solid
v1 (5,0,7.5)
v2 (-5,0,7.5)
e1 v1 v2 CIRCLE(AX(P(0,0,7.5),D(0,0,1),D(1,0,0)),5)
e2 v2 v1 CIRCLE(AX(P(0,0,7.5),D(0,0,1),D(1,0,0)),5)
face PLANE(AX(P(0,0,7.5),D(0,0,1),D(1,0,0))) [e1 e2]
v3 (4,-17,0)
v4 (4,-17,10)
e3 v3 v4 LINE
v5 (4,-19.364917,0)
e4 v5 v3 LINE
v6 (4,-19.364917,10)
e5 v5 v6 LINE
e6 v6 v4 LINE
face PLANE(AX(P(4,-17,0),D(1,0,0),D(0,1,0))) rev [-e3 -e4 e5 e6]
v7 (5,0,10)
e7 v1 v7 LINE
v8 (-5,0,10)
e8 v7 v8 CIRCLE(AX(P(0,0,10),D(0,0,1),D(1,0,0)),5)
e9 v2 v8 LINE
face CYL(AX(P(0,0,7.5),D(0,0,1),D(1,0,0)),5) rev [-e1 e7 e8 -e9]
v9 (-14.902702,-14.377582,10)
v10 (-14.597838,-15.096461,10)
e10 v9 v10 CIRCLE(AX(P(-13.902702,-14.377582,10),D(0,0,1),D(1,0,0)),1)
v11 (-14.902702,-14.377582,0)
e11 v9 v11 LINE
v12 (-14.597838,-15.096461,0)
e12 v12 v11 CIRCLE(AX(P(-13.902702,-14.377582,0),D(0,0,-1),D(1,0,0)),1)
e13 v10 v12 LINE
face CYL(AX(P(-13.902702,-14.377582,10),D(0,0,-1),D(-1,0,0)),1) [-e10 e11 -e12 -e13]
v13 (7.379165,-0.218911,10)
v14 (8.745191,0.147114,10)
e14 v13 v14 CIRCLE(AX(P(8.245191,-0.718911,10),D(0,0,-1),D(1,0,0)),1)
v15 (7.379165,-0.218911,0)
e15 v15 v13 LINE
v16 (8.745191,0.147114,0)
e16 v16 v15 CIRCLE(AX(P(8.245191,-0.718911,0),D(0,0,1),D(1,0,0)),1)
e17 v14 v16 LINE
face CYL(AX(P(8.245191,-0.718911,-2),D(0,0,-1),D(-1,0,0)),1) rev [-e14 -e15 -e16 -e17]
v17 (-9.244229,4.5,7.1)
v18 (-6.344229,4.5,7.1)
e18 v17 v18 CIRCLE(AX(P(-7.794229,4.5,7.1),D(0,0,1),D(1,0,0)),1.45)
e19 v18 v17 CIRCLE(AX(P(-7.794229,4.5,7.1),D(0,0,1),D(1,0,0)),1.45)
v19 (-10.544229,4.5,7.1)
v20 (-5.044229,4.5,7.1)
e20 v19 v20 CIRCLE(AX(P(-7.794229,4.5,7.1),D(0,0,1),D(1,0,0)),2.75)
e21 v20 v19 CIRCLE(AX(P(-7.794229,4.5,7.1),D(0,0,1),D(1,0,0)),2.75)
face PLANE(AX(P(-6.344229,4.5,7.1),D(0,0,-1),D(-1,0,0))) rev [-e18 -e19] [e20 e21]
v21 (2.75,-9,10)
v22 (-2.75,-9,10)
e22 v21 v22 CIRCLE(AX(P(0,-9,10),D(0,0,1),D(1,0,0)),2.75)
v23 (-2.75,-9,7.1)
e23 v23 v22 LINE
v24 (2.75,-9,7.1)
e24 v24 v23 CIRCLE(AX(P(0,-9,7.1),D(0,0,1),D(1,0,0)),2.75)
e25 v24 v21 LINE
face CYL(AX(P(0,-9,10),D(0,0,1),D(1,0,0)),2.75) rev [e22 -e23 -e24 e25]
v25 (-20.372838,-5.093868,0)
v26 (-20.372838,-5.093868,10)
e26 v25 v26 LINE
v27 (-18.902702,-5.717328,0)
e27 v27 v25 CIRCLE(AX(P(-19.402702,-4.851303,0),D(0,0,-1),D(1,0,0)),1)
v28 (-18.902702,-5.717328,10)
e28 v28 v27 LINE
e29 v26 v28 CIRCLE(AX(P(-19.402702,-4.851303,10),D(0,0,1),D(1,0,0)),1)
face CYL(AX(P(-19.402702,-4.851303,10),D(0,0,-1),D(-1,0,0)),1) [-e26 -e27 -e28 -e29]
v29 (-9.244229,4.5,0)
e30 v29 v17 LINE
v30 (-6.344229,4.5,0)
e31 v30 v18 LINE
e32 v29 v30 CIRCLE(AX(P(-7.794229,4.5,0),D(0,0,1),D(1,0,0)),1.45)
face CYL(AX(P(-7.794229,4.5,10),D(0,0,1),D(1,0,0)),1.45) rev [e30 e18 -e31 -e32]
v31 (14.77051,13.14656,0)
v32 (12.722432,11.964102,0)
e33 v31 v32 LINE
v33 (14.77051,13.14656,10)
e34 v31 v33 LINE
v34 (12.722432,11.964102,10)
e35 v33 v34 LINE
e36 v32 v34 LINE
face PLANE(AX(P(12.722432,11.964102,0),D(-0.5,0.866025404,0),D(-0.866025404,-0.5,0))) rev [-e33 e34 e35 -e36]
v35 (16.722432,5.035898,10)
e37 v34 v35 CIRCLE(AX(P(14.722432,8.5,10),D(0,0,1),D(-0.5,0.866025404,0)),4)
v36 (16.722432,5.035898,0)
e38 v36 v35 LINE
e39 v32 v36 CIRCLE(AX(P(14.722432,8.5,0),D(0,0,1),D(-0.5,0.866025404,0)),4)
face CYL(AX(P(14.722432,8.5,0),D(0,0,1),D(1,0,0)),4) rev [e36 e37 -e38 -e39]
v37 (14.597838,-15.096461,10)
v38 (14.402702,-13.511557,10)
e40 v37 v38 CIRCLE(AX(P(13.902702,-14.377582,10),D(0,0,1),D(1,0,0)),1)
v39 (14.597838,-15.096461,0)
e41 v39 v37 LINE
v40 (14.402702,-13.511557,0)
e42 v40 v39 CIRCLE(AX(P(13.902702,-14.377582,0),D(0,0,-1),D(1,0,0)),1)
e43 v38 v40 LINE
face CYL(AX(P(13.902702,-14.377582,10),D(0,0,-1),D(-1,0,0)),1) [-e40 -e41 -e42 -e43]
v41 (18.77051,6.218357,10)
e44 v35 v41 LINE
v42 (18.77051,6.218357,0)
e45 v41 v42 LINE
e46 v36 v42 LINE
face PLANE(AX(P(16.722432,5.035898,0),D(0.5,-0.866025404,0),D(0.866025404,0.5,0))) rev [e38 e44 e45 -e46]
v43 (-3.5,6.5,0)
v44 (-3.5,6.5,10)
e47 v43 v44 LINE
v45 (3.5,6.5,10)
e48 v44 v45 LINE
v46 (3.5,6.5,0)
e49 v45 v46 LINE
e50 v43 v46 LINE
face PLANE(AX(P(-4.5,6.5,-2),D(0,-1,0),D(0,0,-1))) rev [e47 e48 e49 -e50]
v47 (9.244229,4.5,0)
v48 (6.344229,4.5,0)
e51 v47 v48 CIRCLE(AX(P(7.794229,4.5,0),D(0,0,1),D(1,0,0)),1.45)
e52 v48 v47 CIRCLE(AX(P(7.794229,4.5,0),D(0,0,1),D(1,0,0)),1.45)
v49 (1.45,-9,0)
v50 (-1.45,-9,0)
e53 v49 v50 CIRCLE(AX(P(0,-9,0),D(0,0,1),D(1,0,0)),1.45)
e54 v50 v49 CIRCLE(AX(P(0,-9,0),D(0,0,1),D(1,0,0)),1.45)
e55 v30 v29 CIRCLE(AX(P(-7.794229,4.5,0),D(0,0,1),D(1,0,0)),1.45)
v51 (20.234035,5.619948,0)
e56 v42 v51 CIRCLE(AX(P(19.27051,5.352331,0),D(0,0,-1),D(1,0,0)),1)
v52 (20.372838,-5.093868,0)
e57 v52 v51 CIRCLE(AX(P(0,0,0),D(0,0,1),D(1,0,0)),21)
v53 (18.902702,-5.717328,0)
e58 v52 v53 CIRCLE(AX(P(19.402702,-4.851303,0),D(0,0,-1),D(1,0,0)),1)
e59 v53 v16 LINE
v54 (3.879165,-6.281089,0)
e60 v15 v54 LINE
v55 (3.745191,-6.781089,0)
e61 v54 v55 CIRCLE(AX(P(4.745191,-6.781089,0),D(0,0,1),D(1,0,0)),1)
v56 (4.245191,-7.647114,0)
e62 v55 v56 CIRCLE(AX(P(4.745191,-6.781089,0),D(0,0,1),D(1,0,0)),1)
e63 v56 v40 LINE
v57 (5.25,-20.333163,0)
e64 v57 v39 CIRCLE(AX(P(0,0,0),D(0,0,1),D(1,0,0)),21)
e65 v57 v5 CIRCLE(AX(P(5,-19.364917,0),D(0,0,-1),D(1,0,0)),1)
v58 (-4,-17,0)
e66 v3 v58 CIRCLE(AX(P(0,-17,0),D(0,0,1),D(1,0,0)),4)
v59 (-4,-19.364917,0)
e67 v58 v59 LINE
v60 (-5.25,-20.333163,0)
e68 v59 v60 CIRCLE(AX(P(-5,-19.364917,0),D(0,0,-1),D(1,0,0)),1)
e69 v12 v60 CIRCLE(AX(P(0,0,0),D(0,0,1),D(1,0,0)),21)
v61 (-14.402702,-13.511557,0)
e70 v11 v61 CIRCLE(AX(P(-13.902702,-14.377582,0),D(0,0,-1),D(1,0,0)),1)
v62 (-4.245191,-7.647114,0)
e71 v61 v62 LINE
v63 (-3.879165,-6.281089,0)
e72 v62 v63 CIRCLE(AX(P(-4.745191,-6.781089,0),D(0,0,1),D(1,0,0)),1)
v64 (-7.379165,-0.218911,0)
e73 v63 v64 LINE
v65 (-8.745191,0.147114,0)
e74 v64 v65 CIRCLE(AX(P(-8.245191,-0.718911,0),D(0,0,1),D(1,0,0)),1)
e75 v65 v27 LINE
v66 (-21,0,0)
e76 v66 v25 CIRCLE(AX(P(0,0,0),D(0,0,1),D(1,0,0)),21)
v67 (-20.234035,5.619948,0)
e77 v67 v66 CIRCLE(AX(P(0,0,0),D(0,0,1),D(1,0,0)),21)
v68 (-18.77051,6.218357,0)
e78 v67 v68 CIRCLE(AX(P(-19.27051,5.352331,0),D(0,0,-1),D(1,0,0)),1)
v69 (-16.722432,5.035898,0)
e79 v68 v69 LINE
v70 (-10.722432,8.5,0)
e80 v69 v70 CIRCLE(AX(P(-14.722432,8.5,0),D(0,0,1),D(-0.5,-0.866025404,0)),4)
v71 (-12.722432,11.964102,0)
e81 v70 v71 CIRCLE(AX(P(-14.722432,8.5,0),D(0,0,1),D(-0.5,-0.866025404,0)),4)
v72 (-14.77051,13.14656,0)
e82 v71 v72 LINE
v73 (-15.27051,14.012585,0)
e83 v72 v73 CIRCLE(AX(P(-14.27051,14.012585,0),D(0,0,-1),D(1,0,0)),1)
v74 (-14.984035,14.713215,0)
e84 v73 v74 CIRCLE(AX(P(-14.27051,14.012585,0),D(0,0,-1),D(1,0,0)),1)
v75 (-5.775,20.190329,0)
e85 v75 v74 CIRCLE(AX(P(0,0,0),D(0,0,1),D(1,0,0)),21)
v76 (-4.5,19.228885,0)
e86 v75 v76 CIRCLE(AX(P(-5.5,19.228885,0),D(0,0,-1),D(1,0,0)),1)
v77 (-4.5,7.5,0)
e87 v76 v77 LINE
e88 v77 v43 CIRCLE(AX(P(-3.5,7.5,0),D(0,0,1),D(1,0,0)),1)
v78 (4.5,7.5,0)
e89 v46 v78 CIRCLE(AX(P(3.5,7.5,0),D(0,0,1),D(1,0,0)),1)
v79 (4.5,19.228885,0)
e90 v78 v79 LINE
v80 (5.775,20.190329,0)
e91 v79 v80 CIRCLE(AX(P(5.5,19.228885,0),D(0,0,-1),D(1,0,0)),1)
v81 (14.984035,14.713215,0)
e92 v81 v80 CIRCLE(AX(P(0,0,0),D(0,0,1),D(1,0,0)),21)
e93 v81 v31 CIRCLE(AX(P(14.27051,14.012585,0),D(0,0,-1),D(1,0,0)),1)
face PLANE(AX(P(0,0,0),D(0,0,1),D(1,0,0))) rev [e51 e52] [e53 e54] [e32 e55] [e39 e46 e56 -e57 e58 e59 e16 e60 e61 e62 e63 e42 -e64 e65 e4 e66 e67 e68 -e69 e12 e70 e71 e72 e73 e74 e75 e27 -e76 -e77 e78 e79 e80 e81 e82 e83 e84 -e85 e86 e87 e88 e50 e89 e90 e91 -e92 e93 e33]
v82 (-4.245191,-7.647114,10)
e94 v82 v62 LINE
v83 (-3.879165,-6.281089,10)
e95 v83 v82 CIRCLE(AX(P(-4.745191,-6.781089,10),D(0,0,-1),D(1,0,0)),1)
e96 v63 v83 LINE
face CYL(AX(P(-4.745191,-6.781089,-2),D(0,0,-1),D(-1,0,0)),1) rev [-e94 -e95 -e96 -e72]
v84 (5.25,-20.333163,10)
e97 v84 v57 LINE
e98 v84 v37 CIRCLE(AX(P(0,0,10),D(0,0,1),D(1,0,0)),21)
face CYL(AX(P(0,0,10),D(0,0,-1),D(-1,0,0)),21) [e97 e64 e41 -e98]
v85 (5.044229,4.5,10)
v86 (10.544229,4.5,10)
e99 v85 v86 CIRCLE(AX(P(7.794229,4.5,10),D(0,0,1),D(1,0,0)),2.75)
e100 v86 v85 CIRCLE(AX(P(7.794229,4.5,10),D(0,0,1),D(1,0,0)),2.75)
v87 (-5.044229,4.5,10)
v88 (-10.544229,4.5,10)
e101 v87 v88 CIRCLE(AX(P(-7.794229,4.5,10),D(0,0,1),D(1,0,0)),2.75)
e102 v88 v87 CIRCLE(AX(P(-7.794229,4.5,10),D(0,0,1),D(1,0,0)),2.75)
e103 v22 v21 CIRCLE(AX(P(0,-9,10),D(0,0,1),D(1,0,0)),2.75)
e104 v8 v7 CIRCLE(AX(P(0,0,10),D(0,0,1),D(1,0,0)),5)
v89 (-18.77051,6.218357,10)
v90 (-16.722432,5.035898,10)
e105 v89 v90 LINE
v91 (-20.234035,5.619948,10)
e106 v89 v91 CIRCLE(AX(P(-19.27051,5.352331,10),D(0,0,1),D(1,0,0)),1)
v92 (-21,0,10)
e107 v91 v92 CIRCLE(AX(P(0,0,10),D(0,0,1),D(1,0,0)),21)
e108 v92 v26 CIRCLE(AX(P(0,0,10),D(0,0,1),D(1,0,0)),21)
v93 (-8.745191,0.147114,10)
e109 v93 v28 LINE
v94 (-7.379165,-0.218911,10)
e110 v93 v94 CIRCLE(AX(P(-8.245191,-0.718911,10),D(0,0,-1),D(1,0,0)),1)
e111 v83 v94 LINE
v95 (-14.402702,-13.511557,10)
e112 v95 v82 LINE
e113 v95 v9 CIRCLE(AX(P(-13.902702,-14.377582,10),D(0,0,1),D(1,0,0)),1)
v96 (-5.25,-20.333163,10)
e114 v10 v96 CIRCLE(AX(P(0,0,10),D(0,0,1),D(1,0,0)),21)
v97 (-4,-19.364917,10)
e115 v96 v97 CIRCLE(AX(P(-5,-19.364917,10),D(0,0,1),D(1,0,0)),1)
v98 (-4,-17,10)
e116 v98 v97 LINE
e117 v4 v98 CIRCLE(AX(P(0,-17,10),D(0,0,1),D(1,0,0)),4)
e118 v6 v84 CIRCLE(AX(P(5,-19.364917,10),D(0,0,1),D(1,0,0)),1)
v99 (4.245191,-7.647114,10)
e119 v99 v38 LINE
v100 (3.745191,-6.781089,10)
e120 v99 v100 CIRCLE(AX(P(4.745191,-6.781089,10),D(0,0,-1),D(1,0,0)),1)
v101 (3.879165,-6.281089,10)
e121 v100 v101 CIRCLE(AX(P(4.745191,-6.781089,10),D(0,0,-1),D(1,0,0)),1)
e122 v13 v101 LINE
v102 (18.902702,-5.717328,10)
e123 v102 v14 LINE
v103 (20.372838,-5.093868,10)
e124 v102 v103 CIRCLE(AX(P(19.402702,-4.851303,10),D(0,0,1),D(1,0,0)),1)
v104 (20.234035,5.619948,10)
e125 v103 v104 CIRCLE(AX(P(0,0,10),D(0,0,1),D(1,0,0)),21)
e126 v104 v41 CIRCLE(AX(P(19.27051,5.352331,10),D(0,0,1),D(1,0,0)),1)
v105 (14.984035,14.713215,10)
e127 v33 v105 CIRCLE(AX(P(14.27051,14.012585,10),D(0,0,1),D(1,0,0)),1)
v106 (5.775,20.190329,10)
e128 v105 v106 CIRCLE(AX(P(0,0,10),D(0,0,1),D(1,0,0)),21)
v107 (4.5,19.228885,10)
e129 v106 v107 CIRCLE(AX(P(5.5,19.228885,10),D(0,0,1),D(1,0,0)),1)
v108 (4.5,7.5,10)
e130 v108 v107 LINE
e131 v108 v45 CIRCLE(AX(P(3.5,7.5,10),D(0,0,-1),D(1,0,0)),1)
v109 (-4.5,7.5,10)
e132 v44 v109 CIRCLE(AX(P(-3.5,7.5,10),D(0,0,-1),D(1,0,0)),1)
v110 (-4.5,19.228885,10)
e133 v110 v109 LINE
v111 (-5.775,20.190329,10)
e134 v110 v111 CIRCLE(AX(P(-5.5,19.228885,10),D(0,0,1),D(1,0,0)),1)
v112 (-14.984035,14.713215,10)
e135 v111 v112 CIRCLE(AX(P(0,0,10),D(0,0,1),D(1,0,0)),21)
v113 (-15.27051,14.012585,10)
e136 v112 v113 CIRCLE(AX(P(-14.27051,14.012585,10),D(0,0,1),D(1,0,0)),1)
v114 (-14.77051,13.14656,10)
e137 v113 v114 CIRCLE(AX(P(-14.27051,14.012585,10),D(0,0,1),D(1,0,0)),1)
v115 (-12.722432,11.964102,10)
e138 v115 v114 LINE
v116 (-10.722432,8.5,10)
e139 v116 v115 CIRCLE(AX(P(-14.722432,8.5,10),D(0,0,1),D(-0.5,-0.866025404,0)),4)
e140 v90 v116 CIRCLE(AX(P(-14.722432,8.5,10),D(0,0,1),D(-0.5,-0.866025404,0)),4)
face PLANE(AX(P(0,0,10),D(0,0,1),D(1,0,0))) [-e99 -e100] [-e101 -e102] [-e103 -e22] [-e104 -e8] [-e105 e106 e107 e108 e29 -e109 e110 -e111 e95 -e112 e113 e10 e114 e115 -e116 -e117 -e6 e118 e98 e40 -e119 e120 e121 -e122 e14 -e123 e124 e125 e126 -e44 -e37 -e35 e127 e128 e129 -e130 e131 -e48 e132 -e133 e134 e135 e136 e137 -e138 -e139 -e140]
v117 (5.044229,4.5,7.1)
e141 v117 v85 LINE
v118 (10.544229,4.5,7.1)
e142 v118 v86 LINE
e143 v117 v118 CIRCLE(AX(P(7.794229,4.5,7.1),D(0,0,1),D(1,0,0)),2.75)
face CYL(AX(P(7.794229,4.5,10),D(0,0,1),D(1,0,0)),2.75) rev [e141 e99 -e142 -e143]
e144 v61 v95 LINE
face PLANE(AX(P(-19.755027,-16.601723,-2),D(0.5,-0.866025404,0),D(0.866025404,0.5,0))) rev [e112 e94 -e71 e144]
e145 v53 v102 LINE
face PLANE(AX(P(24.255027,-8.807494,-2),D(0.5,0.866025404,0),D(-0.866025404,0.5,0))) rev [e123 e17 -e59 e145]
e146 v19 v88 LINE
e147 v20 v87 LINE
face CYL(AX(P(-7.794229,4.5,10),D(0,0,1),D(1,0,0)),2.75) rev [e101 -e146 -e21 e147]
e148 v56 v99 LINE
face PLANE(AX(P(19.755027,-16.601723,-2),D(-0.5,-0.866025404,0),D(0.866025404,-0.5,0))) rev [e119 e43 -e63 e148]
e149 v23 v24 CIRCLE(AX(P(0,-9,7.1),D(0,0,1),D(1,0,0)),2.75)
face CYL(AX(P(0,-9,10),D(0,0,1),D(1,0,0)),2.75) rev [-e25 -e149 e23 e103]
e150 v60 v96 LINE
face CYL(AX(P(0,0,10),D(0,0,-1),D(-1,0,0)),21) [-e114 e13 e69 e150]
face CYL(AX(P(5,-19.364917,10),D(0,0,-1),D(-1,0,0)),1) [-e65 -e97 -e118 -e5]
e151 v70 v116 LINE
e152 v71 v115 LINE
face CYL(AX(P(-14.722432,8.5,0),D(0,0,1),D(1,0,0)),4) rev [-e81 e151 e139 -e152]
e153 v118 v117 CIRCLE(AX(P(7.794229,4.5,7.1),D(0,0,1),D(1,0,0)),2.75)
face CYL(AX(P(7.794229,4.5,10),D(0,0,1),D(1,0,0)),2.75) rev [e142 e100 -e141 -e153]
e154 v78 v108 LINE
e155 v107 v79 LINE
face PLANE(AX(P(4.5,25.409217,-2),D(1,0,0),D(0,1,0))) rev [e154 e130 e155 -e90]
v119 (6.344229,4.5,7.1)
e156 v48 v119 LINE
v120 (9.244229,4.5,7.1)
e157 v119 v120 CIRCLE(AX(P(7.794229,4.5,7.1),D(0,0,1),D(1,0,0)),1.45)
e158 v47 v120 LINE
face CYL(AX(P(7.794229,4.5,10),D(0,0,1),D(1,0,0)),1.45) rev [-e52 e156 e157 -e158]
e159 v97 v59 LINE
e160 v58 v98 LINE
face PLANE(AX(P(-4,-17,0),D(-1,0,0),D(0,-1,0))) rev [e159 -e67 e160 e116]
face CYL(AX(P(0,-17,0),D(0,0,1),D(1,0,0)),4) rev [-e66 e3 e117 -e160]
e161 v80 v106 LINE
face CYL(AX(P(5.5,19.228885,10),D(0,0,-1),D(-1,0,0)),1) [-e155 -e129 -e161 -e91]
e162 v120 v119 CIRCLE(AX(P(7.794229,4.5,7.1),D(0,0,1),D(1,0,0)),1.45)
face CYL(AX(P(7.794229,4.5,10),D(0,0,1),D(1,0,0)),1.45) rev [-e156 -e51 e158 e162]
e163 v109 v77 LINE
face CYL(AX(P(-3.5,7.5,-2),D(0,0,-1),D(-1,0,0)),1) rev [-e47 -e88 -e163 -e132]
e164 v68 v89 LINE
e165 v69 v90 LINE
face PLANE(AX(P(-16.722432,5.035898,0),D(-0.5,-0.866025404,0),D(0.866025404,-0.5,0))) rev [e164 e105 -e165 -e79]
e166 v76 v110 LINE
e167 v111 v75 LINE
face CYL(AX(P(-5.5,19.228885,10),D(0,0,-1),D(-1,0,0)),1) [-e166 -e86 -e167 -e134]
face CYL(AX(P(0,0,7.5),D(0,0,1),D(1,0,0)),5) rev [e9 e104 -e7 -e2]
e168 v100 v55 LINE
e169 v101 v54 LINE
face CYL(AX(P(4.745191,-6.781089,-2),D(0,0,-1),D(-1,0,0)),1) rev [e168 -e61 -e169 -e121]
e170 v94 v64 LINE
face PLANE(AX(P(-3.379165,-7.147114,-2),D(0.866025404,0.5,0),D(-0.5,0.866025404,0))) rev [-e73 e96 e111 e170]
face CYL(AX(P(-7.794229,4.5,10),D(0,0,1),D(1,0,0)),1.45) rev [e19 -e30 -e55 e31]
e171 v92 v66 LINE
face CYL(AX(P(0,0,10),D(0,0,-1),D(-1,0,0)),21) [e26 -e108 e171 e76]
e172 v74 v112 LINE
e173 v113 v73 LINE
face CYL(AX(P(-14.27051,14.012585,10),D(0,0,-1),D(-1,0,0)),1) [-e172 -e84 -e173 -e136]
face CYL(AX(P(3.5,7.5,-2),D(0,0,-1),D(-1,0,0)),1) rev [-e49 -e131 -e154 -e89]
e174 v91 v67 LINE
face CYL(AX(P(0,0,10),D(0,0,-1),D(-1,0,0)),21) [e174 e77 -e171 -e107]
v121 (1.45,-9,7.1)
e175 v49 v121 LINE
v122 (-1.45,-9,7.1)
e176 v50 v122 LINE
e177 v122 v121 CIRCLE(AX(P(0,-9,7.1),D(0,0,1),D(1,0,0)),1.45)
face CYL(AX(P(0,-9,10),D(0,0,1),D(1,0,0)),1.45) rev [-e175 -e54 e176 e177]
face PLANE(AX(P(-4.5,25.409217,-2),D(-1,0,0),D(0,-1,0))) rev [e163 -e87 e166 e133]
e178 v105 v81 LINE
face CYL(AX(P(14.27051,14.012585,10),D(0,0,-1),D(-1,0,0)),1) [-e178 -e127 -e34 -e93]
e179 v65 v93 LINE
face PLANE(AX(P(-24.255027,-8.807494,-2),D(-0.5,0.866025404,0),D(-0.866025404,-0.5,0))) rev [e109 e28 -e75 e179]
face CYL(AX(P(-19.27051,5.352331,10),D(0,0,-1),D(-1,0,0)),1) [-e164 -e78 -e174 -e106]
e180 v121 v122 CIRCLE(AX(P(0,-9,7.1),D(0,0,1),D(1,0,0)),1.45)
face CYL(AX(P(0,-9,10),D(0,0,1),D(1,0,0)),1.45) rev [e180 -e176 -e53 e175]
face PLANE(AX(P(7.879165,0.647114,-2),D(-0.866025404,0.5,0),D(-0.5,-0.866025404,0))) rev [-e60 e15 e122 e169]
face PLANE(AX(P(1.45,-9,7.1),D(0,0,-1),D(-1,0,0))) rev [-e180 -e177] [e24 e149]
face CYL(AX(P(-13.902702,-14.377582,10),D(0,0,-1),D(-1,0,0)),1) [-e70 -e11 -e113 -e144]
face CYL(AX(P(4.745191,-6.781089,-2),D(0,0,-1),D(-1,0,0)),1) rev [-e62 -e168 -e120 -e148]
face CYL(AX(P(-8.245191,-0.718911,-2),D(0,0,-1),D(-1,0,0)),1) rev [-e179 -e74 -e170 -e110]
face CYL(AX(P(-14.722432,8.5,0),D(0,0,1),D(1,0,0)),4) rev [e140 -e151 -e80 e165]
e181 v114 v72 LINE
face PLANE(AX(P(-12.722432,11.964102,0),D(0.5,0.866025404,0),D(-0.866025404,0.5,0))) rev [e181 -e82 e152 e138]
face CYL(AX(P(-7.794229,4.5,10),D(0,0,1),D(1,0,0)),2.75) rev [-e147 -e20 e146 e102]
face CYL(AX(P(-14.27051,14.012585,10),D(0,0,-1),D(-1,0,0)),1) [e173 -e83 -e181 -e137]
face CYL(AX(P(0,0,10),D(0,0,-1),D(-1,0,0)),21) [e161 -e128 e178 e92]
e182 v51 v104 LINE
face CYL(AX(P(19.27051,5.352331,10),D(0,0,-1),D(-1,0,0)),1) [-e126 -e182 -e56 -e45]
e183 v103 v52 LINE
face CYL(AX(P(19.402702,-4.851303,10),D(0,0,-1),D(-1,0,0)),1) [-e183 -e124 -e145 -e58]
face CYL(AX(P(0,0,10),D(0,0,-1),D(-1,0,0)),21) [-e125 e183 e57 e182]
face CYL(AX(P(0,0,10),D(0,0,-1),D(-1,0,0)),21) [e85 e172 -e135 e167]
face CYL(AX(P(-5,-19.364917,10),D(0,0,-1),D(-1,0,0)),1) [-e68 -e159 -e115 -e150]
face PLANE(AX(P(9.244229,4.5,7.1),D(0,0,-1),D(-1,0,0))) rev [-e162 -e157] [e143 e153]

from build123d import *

# Parameters (mm, degrees)
SKETCH1_R                                            = 21
BOSS_EXTRUDE1_DEPTH                                  = 10
SKETCH2_W                                            = 9
SKETCH2_H                                            = 18.909216571
CUT_EXTRUDE1_DEPTH                                   = 12
FILLET1_R                                            = 1
CIRPATTERN1_COUNT                                    = 3
FILLET1_OF_CIRPATTERN1_R                             = 1
CBORE_FOR_M2_5_HEX_SOCKET_HEAD_CAP_SCREW_D           = 2.9
CBORE_FOR_M2_5_HEX_SOCKET_HEAD_CAP_SCREW_CBORE_D     = 5.5
CBORE_FOR_M2_5_HEX_SOCKET_HEAD_CAP_SCREW_CBORE_DEPTH = 2.9
CIRPATTERN2_COUNT                                    = 3
CUT_EXTRUDE2_DEPTH                                   = 32.336879232
FILLET2_R                                            = 1
CIRPATTERN3_COUNT                                    = 3
FILLET2_OF_CIRPATTERN3_R                             = 1
SKETCH7_R                                            = 5
CUT_EXTRUDE4_DEPTH                                   = 2.5


with BuildPart() as part:
    # Sketch1 → Boss-Extrude1 (new body)
    with BuildSketch(Plane.XY):
        Circle(SKETCH1_R)
    extrude(amount=BOSS_EXTRUDE1_DEPTH)

    # Sketch2 → Cut-Extrude1 (cut)
    with BuildSketch(Plane.XY.offset(10)):
        with Locations((0, 15.954608286)):
            Rectangle(SKETCH2_W, SKETCH2_H)
    cut_extrude1 = extrude(amount=-CUT_EXTRUDE1_DEPTH, mode=Mode.SUBTRACT)

    # Fillet1
    fillet1_edges = [part.edges().sort_by_distance(p)[0] for p in [
        (-4.5, 20.512191497, 5),
        (-4.5, 6.5, 5),
        (4.5, 20.512191497, 5),
        (4.5, 6.5, 5),
    ]]
    fillet(fillet1_edges, radius=FILLET1_R)

    # CirPattern1: Cut-Extrude1 ×3 about axis
    cirpattern1_axis = Axis((0, 0, 0), (0, 0, 1))
    for i in range(1, CIRPATTERN1_COUNT):
        add(cut_extrude1.rotate(cirpattern1_axis, i * 360 / CIRPATTERN1_COUNT), mode=Mode.SUBTRACT)

    # Fillet1 of CirPattern1
    fillet1_of_cirpattern1_edges = [part.edges().sort_by_distance(p)[0] for p in [
        (-15.514078923, -14.153210065, 5),
        (-3.379165125, -7.147114317, 5),
        (-20.014078923, -6.358981431, 5),
        (-7.879165125, 0.647114317, 5),
        (20.014078923, -6.358981431, 5),
        (7.879165125, 0.647114317, 5),
        (15.514078923, -14.153210065, 5),
        (3.379165125, -7.147114317, 5),
    ]]
    fillet(fillet1_of_cirpattern1_edges, radius=FILLET1_OF_CIRPATTERN1_R)

    # CBORE for M2.5 Hex Socket Head Cap Screw1 (through all)
    with Locations(Plane.XY.offset(10)):
        with Locations((0, -9)):
            cbore_for_m2_5_hex_socket_head_cap_screw = CounterBoreHole(CBORE_FOR_M2_5_HEX_SOCKET_HEAD_CAP_SCREW_D / 2, CBORE_FOR_M2_5_HEX_SOCKET_HEAD_CAP_SCREW_CBORE_D / 2, CBORE_FOR_M2_5_HEX_SOCKET_HEAD_CAP_SCREW_CBORE_DEPTH)

    # CirPattern2: CBORE for M2.5 Hex Socket Head Cap Screw1 ×3 about axis
    cirpattern2_axis = Axis((0, 0, 0), (0, 0, 1))
    for i in range(1, CIRPATTERN2_COUNT):
        add(cbore_for_m2_5_hex_socket_head_cap_screw.rotate(cirpattern2_axis, i * 360 / CIRPATTERN2_COUNT), mode=Mode.SUBTRACT)

    # Sketch5 → Cut-Extrude2 (cut, through all)
    with BuildSketch(Plane.XY.offset(10)):
        with BuildLine():
            Line((4, -17), (4, -24.000575883))
            ThreePointArc((4, -24.000575883), (0, -28.000575883), (-4, -24.000575883))
            Line((-4, -24.000575883), (-4, -17))
            ThreePointArc((-4, -17), (0, -13), (4, -17))
        make_face()
    cut_extrude2 = extrude(amount=-CUT_EXTRUDE2_DEPTH, mode=Mode.SUBTRACT)

    # Fillet2
    fillet2_edges = [part.edges().sort_by_distance(p)[0] for p in [
        (4, -20.615528128, 5),
        (-4, -20.615528128, 5),
    ]]
    fillet(fillet2_edges, radius=FILLET2_R)

    # CirPattern3: Cut-Extrude2 ×3 about axis
    cirpattern3_axis = Axis((0, 0, 0), (0, 0, 1))
    for i in range(1, CIRPATTERN3_COUNT):
        add(cut_extrude2.rotate(cirpattern3_axis, i * 360 / CIRPATTERN3_COUNT), mode=Mode.SUBTRACT)

    # Fillet2 of CirPattern3
    fillet2_of_cirpattern3_edges = [part.edges().sort_by_distance(p)[0] for p in [
        (15.853571071, 13.771865679, 5),
        (19.853571071, 6.843662449, 5),
        (-19.853571071, 6.843662449, 5),
        (-15.853571071, 13.771865679, 5),
    ]]
    fillet(fillet2_of_cirpattern3_edges, radius=FILLET2_OF_CIRPATTERN3_R)

    # Sketch7 → Cut-Extrude4 (cut)
    with BuildSketch(Plane.XY.offset(10)):
        Circle(SKETCH7_R)
    extrude(amount=-CUT_EXTRUDE4_DEPTH, mode=Mode.SUBTRACT)


solid = part.part
